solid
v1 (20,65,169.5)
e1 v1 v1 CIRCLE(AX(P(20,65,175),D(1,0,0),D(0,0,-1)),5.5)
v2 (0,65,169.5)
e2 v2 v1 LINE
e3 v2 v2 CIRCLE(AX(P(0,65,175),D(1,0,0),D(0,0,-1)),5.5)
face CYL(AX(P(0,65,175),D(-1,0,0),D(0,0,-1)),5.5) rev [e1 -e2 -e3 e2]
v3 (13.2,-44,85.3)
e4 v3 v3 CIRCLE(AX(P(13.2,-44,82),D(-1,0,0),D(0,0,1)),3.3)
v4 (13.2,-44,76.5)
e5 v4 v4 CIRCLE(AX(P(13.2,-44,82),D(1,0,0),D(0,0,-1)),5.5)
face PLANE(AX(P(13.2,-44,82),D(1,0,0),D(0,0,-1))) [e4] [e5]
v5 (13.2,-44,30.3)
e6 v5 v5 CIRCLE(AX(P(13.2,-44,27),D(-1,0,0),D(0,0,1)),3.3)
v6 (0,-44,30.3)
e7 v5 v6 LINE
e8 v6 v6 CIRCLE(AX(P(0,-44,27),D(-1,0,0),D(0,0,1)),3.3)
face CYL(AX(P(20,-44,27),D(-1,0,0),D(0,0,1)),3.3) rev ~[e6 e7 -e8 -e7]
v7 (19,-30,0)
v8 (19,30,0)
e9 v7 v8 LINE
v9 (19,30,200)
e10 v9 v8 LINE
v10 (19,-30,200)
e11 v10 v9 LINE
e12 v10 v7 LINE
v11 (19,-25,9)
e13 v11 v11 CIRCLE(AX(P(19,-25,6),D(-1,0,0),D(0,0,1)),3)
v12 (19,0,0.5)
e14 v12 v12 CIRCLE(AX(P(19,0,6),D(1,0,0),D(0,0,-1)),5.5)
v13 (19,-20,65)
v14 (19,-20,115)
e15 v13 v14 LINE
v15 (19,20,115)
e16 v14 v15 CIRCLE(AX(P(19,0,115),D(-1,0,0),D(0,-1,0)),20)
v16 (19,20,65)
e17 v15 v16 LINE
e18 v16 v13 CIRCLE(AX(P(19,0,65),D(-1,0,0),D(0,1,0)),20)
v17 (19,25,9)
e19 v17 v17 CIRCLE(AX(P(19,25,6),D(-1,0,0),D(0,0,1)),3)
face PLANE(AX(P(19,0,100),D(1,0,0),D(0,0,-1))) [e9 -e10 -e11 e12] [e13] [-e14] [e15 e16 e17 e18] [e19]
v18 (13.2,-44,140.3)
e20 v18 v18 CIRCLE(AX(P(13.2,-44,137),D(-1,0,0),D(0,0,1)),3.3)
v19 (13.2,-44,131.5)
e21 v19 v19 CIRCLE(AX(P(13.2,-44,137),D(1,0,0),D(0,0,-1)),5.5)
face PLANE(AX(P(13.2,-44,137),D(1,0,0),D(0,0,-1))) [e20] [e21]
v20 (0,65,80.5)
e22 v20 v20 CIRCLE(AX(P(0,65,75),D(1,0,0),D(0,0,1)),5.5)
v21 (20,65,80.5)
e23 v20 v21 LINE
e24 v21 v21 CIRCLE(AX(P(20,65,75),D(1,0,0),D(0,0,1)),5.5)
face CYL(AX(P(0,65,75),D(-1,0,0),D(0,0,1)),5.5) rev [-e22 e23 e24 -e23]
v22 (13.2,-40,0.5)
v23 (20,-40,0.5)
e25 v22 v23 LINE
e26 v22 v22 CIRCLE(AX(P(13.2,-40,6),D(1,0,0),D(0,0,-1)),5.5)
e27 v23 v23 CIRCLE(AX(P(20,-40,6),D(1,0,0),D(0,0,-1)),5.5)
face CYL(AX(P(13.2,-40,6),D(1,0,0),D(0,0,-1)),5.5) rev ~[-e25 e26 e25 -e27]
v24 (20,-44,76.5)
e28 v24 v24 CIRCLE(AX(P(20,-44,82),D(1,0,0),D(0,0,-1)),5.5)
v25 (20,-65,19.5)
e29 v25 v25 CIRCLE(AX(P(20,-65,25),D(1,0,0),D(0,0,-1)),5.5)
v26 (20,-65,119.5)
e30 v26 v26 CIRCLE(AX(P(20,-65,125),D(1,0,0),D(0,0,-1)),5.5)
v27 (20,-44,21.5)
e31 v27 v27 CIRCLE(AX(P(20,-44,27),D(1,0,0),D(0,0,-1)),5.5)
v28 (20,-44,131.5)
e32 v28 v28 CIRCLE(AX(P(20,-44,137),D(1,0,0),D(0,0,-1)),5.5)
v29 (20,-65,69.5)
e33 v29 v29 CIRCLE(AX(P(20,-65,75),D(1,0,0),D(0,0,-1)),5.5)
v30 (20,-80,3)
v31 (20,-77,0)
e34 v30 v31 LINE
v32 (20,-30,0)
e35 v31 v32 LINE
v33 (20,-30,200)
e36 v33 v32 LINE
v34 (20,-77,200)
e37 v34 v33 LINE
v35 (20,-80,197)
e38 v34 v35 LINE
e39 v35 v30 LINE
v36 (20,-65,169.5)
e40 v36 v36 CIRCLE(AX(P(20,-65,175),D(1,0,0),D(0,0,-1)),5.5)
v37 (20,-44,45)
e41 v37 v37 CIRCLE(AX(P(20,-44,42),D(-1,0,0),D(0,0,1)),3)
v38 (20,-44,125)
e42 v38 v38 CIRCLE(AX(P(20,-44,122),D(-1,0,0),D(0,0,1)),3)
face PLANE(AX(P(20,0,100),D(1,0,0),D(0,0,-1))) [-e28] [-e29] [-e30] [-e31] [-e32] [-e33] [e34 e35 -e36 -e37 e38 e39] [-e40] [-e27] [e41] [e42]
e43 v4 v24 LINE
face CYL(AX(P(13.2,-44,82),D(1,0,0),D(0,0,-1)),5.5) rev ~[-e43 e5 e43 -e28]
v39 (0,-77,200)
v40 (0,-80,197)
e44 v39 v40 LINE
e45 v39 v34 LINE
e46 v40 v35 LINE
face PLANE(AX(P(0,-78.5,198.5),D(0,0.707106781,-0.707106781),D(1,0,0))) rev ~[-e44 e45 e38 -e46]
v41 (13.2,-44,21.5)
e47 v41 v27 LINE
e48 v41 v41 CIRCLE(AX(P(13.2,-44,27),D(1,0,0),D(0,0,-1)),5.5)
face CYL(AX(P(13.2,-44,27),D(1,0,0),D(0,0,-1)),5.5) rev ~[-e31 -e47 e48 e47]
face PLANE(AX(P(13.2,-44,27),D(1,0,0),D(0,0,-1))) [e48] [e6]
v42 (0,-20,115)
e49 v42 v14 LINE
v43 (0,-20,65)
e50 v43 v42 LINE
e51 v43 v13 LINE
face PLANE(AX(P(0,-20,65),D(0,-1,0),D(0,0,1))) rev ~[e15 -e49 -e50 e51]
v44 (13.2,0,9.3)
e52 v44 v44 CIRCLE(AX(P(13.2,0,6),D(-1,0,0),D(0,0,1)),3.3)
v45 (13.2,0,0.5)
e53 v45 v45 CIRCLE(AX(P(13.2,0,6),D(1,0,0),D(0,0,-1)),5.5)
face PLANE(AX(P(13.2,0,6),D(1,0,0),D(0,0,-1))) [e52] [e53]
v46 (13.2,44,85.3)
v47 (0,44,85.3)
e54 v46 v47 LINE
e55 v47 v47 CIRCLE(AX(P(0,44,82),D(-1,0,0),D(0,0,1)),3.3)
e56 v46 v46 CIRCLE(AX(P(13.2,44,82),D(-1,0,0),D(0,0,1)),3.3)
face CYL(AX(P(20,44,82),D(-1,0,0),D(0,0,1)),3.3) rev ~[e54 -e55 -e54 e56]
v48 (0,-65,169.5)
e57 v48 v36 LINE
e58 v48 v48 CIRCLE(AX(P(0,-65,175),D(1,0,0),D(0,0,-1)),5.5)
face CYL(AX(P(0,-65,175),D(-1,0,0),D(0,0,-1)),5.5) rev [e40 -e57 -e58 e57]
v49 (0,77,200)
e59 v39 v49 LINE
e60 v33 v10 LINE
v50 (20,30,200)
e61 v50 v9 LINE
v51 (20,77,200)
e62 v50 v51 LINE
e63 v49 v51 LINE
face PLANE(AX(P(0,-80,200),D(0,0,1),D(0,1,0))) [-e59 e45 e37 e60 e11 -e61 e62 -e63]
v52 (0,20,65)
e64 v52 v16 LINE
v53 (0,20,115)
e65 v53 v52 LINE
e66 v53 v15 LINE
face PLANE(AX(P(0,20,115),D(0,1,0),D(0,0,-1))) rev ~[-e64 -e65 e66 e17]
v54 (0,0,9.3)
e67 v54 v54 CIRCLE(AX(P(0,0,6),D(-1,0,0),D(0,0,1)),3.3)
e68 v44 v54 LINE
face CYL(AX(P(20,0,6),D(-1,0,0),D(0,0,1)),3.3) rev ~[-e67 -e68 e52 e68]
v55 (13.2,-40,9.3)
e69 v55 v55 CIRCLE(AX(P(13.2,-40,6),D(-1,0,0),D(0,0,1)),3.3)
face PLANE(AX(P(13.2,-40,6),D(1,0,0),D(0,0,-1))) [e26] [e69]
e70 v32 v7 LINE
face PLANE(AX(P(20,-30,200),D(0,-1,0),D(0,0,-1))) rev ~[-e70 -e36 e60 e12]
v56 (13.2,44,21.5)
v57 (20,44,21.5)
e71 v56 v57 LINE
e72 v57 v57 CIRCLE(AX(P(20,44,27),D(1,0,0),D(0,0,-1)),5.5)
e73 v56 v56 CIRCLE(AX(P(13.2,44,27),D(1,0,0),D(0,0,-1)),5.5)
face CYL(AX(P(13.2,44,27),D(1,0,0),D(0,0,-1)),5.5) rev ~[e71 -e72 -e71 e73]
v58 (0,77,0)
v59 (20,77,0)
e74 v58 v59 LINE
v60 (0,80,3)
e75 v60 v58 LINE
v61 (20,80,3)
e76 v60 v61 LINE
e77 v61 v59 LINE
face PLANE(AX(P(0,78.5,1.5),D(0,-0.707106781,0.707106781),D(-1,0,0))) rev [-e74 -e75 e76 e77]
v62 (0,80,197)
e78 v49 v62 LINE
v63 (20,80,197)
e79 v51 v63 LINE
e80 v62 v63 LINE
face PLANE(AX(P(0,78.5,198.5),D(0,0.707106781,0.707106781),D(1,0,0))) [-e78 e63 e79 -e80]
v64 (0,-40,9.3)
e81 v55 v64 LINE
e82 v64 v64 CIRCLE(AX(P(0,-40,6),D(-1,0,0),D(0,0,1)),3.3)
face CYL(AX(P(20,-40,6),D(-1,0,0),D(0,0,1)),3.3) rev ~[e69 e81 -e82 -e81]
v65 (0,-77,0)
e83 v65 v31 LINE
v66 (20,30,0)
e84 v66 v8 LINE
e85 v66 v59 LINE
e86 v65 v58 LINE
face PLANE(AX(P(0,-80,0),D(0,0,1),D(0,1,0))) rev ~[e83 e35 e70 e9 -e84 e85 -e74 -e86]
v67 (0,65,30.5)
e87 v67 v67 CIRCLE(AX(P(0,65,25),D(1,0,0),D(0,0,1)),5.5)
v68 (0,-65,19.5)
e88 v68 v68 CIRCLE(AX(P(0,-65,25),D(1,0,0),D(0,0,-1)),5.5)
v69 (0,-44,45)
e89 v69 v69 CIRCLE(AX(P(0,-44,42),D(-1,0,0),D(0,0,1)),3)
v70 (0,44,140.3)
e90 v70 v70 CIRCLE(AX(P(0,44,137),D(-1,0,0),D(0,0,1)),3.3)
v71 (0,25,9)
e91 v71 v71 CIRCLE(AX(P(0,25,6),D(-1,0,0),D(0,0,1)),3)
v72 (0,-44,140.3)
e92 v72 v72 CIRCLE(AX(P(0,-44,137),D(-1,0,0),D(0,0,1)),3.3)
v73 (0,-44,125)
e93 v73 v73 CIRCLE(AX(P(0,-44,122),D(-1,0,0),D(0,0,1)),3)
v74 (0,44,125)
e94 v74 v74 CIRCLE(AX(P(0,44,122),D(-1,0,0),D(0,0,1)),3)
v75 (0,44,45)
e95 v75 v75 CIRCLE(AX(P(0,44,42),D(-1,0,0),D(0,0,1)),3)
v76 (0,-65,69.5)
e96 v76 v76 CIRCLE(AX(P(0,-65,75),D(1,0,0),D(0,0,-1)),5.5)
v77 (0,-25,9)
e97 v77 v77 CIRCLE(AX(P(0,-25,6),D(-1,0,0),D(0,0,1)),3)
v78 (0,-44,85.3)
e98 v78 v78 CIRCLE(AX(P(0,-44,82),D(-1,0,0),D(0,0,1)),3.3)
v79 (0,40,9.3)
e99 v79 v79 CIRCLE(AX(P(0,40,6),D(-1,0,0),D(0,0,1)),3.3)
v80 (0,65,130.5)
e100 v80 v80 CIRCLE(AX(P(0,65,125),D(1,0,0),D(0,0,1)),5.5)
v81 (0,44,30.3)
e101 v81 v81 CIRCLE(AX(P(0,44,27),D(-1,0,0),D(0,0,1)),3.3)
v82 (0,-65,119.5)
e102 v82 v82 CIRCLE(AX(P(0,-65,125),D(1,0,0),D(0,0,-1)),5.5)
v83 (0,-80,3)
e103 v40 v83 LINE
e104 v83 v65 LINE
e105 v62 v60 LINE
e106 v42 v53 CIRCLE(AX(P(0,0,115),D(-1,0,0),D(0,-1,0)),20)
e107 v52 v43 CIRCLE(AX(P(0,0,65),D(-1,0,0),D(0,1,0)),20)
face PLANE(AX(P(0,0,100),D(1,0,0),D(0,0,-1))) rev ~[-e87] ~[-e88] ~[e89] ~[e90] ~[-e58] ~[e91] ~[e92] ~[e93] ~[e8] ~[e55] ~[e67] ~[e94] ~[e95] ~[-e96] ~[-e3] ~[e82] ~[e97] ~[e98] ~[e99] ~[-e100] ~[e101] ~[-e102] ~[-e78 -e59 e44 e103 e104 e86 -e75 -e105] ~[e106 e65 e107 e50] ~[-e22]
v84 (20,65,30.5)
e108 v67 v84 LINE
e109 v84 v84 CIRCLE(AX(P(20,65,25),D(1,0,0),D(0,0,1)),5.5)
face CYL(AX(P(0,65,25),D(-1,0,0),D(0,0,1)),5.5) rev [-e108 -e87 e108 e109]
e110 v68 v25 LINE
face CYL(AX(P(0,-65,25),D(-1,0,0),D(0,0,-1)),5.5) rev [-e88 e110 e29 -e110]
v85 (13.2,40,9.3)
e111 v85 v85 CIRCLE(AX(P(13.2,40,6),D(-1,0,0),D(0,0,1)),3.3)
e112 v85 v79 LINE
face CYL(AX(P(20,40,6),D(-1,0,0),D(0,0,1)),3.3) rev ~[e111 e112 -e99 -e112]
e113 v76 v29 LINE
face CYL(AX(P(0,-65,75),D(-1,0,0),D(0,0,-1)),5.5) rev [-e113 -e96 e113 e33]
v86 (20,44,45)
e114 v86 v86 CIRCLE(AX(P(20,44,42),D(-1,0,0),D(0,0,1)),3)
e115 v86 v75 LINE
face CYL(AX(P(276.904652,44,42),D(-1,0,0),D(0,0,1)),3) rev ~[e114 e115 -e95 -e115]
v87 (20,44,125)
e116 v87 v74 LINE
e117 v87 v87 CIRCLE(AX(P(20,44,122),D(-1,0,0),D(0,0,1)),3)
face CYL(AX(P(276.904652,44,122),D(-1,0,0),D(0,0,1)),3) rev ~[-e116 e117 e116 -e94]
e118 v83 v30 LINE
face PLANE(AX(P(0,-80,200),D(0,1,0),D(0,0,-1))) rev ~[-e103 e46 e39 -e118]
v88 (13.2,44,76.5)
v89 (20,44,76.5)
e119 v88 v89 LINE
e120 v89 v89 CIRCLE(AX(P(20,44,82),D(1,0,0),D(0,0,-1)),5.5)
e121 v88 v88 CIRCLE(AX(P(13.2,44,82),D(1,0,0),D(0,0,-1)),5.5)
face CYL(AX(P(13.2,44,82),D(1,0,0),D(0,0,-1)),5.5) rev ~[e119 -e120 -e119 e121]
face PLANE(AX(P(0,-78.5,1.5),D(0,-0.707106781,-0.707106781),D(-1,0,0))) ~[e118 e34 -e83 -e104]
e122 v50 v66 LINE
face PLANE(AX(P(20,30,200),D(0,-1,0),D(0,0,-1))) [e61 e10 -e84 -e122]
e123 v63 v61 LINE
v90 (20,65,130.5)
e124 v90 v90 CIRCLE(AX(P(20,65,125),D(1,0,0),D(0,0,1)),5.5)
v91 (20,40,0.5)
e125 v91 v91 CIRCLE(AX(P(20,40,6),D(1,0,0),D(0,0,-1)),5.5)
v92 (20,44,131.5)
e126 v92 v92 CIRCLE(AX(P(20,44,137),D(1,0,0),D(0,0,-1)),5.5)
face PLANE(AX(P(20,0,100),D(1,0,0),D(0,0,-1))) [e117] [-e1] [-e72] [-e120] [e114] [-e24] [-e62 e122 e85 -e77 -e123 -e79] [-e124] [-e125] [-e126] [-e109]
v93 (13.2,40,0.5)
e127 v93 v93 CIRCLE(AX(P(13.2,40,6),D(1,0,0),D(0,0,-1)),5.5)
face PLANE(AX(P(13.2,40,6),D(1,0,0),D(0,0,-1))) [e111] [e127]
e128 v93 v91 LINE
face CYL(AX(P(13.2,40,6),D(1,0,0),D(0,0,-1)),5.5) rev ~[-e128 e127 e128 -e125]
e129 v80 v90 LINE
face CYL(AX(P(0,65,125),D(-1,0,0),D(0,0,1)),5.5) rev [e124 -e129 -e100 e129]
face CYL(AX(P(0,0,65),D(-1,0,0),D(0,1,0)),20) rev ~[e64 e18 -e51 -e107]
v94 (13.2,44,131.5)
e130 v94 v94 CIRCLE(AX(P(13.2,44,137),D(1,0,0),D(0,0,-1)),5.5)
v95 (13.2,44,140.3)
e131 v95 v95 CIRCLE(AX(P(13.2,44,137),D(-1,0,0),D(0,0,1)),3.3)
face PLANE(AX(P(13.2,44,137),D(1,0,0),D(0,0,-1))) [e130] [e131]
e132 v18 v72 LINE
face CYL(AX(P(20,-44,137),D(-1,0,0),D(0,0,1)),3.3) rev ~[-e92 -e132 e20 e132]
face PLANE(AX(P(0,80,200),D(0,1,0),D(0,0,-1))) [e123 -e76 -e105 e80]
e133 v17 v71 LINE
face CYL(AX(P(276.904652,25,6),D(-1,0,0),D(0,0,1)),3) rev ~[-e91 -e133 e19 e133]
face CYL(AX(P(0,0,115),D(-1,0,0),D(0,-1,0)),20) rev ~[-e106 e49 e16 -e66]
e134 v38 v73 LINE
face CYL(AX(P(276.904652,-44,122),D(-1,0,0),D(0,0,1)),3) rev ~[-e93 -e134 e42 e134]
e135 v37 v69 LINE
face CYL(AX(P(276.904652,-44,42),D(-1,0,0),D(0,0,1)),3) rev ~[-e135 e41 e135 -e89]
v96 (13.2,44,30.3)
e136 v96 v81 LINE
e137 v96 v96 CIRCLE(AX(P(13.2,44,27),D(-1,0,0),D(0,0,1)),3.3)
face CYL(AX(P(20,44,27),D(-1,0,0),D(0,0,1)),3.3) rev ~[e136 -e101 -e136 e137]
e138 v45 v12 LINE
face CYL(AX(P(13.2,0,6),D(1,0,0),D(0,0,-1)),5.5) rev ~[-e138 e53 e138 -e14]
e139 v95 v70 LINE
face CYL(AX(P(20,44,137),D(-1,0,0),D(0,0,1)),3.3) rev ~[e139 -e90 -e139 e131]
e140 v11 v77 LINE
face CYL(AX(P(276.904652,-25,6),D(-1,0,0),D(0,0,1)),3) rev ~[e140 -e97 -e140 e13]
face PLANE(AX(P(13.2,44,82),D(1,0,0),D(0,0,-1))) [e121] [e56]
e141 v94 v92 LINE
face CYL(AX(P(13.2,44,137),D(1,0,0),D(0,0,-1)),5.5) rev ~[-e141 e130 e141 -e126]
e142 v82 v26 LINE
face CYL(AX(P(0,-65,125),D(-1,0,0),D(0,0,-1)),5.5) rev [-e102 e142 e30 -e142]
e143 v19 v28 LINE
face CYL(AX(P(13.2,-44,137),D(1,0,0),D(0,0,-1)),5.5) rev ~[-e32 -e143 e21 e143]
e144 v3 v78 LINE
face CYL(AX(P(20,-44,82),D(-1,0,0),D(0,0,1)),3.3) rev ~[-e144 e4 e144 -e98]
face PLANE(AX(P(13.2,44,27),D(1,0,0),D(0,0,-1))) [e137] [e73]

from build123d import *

# Parameters (mm, degrees)
SKETCH4_W                                        = 200
SKETCH4_H                                        = 160
SKETCH4_R                                        = 5.5
BOSS_EXTRUDE4_DEPTH                              = 20
HOLE_SIZE_PER_HEX_SOCKET_SCREW_TYPE1_D           = 6.6
HOLE_SIZE_PER_HEX_SOCKET_SCREW_TYPE1_CBORE_D     = 11
HOLE_SIZE_PER_HEX_SOCKET_SCREW_TYPE1_CBORE_DEPTH = 6.8
F_6_0_6_DIAMETER_HOLE1_D                         = 6
SKETCH10_W                                       = 200
SKETCH10_H                                       = 60
CUT_EXTRUDE4_DEPTH                               = 1
CHAMFER1_SIZE                                    = 3


with BuildPart() as part:
    # Sketch4 → Boss-Extrude4 (new body)
    with BuildSketch(Plane(origin=(0, 0, 0), x_dir=(0, 0, -1), z_dir=(1, 0, 0))):
        with Locations((-100, 0)):
            Rectangle(SKETCH4_W, SKETCH4_H)
        with Locations((-125, -65)):
            Circle(SKETCH4_R, mode=Mode.SUBTRACT)
        with Locations((-75, -65)):
            Circle(SKETCH4_R, mode=Mode.SUBTRACT)
        with Locations((-25, -65)):
            Circle(SKETCH4_R, mode=Mode.SUBTRACT)
        with Locations(Location((-125, 65, 0), (0, 0, 180))):
            Circle(SKETCH4_R, mode=Mode.SUBTRACT)
        with Locations(Location((-75, 65, 0), (0, 0, 180))):
            Circle(SKETCH4_R, mode=Mode.SUBTRACT)
        with Locations(Location((-25, 65, 0), (0, 0, 180))):
            Circle(SKETCH4_R, mode=Mode.SUBTRACT)
        with Locations((-175, -65)):
            Circle(SKETCH4_R, mode=Mode.SUBTRACT)
        with Locations((-175, 65)):
            Circle(SKETCH4_R, mode=Mode.SUBTRACT)
        with BuildLine():
            Line((-65, -20), (-115, -20))
            ThreePointArc((-115, -20), (-135, 0), (-115, 20))
            Line((-115, 20), (-65, 20))
            ThreePointArc((-65, 20), (-45, 0), (-65, -20))
        make_face(mode=Mode.SUBTRACT)
    extrude(amount=BOSS_EXTRUDE4_DEPTH)

    # Hole size per hex socket screw type1 (through all)
    with Locations(Plane(origin=(20, 0, 0), x_dir=(0, 0, -1), z_dir=(1, 0, 0))):
        with Locations((-6, 40), (-6, 0), (-6, -40), (-27, -44), (-82, -44), (-137, -44), (-27, 44), (-82, 44), (-137, 44)):
            CounterBoreHole(HOLE_SIZE_PER_HEX_SOCKET_SCREW_TYPE1_D / 2, HOLE_SIZE_PER_HEX_SOCKET_SCREW_TYPE1_CBORE_D / 2, HOLE_SIZE_PER_HEX_SOCKET_SCREW_TYPE1_CBORE_DEPTH)

    # Ø6.0 (6) Diameter Hole1 (through all)
    with Locations(Plane(origin=(20, 0, 0), x_dir=(0, 0, -1), z_dir=(1, 0, 0))):
        with Locations((-6, 25), (-6, -25), (-42, -44), (-122, -44), (-122, 44), (-42, 44)):
            Hole(F_6_0_6_DIAMETER_HOLE1_D / 2)

    # Sketch10 → Cut-Extrude4 (cut)
    with BuildSketch(Plane(origin=(20, 0, 0), x_dir=(0, 0, -1), z_dir=(1, 0, 0))):
        with Locations((-100, 0)):
            Rectangle(SKETCH10_W, SKETCH10_H)
    extrude(amount=-CUT_EXTRUDE4_DEPTH, mode=Mode.SUBTRACT)

    # Chamfer1
    chamfer1_edges = [part.edges().sort_by_distance(p)[0] for p in [
        (10, 80, 200),
        (10, 80, 0),
        (10, -80, 0),
        (10, -80, 200),
    ]]
    chamfer(chamfer1_edges, length=CHAMFER1_SIZE)


solid = part.part
